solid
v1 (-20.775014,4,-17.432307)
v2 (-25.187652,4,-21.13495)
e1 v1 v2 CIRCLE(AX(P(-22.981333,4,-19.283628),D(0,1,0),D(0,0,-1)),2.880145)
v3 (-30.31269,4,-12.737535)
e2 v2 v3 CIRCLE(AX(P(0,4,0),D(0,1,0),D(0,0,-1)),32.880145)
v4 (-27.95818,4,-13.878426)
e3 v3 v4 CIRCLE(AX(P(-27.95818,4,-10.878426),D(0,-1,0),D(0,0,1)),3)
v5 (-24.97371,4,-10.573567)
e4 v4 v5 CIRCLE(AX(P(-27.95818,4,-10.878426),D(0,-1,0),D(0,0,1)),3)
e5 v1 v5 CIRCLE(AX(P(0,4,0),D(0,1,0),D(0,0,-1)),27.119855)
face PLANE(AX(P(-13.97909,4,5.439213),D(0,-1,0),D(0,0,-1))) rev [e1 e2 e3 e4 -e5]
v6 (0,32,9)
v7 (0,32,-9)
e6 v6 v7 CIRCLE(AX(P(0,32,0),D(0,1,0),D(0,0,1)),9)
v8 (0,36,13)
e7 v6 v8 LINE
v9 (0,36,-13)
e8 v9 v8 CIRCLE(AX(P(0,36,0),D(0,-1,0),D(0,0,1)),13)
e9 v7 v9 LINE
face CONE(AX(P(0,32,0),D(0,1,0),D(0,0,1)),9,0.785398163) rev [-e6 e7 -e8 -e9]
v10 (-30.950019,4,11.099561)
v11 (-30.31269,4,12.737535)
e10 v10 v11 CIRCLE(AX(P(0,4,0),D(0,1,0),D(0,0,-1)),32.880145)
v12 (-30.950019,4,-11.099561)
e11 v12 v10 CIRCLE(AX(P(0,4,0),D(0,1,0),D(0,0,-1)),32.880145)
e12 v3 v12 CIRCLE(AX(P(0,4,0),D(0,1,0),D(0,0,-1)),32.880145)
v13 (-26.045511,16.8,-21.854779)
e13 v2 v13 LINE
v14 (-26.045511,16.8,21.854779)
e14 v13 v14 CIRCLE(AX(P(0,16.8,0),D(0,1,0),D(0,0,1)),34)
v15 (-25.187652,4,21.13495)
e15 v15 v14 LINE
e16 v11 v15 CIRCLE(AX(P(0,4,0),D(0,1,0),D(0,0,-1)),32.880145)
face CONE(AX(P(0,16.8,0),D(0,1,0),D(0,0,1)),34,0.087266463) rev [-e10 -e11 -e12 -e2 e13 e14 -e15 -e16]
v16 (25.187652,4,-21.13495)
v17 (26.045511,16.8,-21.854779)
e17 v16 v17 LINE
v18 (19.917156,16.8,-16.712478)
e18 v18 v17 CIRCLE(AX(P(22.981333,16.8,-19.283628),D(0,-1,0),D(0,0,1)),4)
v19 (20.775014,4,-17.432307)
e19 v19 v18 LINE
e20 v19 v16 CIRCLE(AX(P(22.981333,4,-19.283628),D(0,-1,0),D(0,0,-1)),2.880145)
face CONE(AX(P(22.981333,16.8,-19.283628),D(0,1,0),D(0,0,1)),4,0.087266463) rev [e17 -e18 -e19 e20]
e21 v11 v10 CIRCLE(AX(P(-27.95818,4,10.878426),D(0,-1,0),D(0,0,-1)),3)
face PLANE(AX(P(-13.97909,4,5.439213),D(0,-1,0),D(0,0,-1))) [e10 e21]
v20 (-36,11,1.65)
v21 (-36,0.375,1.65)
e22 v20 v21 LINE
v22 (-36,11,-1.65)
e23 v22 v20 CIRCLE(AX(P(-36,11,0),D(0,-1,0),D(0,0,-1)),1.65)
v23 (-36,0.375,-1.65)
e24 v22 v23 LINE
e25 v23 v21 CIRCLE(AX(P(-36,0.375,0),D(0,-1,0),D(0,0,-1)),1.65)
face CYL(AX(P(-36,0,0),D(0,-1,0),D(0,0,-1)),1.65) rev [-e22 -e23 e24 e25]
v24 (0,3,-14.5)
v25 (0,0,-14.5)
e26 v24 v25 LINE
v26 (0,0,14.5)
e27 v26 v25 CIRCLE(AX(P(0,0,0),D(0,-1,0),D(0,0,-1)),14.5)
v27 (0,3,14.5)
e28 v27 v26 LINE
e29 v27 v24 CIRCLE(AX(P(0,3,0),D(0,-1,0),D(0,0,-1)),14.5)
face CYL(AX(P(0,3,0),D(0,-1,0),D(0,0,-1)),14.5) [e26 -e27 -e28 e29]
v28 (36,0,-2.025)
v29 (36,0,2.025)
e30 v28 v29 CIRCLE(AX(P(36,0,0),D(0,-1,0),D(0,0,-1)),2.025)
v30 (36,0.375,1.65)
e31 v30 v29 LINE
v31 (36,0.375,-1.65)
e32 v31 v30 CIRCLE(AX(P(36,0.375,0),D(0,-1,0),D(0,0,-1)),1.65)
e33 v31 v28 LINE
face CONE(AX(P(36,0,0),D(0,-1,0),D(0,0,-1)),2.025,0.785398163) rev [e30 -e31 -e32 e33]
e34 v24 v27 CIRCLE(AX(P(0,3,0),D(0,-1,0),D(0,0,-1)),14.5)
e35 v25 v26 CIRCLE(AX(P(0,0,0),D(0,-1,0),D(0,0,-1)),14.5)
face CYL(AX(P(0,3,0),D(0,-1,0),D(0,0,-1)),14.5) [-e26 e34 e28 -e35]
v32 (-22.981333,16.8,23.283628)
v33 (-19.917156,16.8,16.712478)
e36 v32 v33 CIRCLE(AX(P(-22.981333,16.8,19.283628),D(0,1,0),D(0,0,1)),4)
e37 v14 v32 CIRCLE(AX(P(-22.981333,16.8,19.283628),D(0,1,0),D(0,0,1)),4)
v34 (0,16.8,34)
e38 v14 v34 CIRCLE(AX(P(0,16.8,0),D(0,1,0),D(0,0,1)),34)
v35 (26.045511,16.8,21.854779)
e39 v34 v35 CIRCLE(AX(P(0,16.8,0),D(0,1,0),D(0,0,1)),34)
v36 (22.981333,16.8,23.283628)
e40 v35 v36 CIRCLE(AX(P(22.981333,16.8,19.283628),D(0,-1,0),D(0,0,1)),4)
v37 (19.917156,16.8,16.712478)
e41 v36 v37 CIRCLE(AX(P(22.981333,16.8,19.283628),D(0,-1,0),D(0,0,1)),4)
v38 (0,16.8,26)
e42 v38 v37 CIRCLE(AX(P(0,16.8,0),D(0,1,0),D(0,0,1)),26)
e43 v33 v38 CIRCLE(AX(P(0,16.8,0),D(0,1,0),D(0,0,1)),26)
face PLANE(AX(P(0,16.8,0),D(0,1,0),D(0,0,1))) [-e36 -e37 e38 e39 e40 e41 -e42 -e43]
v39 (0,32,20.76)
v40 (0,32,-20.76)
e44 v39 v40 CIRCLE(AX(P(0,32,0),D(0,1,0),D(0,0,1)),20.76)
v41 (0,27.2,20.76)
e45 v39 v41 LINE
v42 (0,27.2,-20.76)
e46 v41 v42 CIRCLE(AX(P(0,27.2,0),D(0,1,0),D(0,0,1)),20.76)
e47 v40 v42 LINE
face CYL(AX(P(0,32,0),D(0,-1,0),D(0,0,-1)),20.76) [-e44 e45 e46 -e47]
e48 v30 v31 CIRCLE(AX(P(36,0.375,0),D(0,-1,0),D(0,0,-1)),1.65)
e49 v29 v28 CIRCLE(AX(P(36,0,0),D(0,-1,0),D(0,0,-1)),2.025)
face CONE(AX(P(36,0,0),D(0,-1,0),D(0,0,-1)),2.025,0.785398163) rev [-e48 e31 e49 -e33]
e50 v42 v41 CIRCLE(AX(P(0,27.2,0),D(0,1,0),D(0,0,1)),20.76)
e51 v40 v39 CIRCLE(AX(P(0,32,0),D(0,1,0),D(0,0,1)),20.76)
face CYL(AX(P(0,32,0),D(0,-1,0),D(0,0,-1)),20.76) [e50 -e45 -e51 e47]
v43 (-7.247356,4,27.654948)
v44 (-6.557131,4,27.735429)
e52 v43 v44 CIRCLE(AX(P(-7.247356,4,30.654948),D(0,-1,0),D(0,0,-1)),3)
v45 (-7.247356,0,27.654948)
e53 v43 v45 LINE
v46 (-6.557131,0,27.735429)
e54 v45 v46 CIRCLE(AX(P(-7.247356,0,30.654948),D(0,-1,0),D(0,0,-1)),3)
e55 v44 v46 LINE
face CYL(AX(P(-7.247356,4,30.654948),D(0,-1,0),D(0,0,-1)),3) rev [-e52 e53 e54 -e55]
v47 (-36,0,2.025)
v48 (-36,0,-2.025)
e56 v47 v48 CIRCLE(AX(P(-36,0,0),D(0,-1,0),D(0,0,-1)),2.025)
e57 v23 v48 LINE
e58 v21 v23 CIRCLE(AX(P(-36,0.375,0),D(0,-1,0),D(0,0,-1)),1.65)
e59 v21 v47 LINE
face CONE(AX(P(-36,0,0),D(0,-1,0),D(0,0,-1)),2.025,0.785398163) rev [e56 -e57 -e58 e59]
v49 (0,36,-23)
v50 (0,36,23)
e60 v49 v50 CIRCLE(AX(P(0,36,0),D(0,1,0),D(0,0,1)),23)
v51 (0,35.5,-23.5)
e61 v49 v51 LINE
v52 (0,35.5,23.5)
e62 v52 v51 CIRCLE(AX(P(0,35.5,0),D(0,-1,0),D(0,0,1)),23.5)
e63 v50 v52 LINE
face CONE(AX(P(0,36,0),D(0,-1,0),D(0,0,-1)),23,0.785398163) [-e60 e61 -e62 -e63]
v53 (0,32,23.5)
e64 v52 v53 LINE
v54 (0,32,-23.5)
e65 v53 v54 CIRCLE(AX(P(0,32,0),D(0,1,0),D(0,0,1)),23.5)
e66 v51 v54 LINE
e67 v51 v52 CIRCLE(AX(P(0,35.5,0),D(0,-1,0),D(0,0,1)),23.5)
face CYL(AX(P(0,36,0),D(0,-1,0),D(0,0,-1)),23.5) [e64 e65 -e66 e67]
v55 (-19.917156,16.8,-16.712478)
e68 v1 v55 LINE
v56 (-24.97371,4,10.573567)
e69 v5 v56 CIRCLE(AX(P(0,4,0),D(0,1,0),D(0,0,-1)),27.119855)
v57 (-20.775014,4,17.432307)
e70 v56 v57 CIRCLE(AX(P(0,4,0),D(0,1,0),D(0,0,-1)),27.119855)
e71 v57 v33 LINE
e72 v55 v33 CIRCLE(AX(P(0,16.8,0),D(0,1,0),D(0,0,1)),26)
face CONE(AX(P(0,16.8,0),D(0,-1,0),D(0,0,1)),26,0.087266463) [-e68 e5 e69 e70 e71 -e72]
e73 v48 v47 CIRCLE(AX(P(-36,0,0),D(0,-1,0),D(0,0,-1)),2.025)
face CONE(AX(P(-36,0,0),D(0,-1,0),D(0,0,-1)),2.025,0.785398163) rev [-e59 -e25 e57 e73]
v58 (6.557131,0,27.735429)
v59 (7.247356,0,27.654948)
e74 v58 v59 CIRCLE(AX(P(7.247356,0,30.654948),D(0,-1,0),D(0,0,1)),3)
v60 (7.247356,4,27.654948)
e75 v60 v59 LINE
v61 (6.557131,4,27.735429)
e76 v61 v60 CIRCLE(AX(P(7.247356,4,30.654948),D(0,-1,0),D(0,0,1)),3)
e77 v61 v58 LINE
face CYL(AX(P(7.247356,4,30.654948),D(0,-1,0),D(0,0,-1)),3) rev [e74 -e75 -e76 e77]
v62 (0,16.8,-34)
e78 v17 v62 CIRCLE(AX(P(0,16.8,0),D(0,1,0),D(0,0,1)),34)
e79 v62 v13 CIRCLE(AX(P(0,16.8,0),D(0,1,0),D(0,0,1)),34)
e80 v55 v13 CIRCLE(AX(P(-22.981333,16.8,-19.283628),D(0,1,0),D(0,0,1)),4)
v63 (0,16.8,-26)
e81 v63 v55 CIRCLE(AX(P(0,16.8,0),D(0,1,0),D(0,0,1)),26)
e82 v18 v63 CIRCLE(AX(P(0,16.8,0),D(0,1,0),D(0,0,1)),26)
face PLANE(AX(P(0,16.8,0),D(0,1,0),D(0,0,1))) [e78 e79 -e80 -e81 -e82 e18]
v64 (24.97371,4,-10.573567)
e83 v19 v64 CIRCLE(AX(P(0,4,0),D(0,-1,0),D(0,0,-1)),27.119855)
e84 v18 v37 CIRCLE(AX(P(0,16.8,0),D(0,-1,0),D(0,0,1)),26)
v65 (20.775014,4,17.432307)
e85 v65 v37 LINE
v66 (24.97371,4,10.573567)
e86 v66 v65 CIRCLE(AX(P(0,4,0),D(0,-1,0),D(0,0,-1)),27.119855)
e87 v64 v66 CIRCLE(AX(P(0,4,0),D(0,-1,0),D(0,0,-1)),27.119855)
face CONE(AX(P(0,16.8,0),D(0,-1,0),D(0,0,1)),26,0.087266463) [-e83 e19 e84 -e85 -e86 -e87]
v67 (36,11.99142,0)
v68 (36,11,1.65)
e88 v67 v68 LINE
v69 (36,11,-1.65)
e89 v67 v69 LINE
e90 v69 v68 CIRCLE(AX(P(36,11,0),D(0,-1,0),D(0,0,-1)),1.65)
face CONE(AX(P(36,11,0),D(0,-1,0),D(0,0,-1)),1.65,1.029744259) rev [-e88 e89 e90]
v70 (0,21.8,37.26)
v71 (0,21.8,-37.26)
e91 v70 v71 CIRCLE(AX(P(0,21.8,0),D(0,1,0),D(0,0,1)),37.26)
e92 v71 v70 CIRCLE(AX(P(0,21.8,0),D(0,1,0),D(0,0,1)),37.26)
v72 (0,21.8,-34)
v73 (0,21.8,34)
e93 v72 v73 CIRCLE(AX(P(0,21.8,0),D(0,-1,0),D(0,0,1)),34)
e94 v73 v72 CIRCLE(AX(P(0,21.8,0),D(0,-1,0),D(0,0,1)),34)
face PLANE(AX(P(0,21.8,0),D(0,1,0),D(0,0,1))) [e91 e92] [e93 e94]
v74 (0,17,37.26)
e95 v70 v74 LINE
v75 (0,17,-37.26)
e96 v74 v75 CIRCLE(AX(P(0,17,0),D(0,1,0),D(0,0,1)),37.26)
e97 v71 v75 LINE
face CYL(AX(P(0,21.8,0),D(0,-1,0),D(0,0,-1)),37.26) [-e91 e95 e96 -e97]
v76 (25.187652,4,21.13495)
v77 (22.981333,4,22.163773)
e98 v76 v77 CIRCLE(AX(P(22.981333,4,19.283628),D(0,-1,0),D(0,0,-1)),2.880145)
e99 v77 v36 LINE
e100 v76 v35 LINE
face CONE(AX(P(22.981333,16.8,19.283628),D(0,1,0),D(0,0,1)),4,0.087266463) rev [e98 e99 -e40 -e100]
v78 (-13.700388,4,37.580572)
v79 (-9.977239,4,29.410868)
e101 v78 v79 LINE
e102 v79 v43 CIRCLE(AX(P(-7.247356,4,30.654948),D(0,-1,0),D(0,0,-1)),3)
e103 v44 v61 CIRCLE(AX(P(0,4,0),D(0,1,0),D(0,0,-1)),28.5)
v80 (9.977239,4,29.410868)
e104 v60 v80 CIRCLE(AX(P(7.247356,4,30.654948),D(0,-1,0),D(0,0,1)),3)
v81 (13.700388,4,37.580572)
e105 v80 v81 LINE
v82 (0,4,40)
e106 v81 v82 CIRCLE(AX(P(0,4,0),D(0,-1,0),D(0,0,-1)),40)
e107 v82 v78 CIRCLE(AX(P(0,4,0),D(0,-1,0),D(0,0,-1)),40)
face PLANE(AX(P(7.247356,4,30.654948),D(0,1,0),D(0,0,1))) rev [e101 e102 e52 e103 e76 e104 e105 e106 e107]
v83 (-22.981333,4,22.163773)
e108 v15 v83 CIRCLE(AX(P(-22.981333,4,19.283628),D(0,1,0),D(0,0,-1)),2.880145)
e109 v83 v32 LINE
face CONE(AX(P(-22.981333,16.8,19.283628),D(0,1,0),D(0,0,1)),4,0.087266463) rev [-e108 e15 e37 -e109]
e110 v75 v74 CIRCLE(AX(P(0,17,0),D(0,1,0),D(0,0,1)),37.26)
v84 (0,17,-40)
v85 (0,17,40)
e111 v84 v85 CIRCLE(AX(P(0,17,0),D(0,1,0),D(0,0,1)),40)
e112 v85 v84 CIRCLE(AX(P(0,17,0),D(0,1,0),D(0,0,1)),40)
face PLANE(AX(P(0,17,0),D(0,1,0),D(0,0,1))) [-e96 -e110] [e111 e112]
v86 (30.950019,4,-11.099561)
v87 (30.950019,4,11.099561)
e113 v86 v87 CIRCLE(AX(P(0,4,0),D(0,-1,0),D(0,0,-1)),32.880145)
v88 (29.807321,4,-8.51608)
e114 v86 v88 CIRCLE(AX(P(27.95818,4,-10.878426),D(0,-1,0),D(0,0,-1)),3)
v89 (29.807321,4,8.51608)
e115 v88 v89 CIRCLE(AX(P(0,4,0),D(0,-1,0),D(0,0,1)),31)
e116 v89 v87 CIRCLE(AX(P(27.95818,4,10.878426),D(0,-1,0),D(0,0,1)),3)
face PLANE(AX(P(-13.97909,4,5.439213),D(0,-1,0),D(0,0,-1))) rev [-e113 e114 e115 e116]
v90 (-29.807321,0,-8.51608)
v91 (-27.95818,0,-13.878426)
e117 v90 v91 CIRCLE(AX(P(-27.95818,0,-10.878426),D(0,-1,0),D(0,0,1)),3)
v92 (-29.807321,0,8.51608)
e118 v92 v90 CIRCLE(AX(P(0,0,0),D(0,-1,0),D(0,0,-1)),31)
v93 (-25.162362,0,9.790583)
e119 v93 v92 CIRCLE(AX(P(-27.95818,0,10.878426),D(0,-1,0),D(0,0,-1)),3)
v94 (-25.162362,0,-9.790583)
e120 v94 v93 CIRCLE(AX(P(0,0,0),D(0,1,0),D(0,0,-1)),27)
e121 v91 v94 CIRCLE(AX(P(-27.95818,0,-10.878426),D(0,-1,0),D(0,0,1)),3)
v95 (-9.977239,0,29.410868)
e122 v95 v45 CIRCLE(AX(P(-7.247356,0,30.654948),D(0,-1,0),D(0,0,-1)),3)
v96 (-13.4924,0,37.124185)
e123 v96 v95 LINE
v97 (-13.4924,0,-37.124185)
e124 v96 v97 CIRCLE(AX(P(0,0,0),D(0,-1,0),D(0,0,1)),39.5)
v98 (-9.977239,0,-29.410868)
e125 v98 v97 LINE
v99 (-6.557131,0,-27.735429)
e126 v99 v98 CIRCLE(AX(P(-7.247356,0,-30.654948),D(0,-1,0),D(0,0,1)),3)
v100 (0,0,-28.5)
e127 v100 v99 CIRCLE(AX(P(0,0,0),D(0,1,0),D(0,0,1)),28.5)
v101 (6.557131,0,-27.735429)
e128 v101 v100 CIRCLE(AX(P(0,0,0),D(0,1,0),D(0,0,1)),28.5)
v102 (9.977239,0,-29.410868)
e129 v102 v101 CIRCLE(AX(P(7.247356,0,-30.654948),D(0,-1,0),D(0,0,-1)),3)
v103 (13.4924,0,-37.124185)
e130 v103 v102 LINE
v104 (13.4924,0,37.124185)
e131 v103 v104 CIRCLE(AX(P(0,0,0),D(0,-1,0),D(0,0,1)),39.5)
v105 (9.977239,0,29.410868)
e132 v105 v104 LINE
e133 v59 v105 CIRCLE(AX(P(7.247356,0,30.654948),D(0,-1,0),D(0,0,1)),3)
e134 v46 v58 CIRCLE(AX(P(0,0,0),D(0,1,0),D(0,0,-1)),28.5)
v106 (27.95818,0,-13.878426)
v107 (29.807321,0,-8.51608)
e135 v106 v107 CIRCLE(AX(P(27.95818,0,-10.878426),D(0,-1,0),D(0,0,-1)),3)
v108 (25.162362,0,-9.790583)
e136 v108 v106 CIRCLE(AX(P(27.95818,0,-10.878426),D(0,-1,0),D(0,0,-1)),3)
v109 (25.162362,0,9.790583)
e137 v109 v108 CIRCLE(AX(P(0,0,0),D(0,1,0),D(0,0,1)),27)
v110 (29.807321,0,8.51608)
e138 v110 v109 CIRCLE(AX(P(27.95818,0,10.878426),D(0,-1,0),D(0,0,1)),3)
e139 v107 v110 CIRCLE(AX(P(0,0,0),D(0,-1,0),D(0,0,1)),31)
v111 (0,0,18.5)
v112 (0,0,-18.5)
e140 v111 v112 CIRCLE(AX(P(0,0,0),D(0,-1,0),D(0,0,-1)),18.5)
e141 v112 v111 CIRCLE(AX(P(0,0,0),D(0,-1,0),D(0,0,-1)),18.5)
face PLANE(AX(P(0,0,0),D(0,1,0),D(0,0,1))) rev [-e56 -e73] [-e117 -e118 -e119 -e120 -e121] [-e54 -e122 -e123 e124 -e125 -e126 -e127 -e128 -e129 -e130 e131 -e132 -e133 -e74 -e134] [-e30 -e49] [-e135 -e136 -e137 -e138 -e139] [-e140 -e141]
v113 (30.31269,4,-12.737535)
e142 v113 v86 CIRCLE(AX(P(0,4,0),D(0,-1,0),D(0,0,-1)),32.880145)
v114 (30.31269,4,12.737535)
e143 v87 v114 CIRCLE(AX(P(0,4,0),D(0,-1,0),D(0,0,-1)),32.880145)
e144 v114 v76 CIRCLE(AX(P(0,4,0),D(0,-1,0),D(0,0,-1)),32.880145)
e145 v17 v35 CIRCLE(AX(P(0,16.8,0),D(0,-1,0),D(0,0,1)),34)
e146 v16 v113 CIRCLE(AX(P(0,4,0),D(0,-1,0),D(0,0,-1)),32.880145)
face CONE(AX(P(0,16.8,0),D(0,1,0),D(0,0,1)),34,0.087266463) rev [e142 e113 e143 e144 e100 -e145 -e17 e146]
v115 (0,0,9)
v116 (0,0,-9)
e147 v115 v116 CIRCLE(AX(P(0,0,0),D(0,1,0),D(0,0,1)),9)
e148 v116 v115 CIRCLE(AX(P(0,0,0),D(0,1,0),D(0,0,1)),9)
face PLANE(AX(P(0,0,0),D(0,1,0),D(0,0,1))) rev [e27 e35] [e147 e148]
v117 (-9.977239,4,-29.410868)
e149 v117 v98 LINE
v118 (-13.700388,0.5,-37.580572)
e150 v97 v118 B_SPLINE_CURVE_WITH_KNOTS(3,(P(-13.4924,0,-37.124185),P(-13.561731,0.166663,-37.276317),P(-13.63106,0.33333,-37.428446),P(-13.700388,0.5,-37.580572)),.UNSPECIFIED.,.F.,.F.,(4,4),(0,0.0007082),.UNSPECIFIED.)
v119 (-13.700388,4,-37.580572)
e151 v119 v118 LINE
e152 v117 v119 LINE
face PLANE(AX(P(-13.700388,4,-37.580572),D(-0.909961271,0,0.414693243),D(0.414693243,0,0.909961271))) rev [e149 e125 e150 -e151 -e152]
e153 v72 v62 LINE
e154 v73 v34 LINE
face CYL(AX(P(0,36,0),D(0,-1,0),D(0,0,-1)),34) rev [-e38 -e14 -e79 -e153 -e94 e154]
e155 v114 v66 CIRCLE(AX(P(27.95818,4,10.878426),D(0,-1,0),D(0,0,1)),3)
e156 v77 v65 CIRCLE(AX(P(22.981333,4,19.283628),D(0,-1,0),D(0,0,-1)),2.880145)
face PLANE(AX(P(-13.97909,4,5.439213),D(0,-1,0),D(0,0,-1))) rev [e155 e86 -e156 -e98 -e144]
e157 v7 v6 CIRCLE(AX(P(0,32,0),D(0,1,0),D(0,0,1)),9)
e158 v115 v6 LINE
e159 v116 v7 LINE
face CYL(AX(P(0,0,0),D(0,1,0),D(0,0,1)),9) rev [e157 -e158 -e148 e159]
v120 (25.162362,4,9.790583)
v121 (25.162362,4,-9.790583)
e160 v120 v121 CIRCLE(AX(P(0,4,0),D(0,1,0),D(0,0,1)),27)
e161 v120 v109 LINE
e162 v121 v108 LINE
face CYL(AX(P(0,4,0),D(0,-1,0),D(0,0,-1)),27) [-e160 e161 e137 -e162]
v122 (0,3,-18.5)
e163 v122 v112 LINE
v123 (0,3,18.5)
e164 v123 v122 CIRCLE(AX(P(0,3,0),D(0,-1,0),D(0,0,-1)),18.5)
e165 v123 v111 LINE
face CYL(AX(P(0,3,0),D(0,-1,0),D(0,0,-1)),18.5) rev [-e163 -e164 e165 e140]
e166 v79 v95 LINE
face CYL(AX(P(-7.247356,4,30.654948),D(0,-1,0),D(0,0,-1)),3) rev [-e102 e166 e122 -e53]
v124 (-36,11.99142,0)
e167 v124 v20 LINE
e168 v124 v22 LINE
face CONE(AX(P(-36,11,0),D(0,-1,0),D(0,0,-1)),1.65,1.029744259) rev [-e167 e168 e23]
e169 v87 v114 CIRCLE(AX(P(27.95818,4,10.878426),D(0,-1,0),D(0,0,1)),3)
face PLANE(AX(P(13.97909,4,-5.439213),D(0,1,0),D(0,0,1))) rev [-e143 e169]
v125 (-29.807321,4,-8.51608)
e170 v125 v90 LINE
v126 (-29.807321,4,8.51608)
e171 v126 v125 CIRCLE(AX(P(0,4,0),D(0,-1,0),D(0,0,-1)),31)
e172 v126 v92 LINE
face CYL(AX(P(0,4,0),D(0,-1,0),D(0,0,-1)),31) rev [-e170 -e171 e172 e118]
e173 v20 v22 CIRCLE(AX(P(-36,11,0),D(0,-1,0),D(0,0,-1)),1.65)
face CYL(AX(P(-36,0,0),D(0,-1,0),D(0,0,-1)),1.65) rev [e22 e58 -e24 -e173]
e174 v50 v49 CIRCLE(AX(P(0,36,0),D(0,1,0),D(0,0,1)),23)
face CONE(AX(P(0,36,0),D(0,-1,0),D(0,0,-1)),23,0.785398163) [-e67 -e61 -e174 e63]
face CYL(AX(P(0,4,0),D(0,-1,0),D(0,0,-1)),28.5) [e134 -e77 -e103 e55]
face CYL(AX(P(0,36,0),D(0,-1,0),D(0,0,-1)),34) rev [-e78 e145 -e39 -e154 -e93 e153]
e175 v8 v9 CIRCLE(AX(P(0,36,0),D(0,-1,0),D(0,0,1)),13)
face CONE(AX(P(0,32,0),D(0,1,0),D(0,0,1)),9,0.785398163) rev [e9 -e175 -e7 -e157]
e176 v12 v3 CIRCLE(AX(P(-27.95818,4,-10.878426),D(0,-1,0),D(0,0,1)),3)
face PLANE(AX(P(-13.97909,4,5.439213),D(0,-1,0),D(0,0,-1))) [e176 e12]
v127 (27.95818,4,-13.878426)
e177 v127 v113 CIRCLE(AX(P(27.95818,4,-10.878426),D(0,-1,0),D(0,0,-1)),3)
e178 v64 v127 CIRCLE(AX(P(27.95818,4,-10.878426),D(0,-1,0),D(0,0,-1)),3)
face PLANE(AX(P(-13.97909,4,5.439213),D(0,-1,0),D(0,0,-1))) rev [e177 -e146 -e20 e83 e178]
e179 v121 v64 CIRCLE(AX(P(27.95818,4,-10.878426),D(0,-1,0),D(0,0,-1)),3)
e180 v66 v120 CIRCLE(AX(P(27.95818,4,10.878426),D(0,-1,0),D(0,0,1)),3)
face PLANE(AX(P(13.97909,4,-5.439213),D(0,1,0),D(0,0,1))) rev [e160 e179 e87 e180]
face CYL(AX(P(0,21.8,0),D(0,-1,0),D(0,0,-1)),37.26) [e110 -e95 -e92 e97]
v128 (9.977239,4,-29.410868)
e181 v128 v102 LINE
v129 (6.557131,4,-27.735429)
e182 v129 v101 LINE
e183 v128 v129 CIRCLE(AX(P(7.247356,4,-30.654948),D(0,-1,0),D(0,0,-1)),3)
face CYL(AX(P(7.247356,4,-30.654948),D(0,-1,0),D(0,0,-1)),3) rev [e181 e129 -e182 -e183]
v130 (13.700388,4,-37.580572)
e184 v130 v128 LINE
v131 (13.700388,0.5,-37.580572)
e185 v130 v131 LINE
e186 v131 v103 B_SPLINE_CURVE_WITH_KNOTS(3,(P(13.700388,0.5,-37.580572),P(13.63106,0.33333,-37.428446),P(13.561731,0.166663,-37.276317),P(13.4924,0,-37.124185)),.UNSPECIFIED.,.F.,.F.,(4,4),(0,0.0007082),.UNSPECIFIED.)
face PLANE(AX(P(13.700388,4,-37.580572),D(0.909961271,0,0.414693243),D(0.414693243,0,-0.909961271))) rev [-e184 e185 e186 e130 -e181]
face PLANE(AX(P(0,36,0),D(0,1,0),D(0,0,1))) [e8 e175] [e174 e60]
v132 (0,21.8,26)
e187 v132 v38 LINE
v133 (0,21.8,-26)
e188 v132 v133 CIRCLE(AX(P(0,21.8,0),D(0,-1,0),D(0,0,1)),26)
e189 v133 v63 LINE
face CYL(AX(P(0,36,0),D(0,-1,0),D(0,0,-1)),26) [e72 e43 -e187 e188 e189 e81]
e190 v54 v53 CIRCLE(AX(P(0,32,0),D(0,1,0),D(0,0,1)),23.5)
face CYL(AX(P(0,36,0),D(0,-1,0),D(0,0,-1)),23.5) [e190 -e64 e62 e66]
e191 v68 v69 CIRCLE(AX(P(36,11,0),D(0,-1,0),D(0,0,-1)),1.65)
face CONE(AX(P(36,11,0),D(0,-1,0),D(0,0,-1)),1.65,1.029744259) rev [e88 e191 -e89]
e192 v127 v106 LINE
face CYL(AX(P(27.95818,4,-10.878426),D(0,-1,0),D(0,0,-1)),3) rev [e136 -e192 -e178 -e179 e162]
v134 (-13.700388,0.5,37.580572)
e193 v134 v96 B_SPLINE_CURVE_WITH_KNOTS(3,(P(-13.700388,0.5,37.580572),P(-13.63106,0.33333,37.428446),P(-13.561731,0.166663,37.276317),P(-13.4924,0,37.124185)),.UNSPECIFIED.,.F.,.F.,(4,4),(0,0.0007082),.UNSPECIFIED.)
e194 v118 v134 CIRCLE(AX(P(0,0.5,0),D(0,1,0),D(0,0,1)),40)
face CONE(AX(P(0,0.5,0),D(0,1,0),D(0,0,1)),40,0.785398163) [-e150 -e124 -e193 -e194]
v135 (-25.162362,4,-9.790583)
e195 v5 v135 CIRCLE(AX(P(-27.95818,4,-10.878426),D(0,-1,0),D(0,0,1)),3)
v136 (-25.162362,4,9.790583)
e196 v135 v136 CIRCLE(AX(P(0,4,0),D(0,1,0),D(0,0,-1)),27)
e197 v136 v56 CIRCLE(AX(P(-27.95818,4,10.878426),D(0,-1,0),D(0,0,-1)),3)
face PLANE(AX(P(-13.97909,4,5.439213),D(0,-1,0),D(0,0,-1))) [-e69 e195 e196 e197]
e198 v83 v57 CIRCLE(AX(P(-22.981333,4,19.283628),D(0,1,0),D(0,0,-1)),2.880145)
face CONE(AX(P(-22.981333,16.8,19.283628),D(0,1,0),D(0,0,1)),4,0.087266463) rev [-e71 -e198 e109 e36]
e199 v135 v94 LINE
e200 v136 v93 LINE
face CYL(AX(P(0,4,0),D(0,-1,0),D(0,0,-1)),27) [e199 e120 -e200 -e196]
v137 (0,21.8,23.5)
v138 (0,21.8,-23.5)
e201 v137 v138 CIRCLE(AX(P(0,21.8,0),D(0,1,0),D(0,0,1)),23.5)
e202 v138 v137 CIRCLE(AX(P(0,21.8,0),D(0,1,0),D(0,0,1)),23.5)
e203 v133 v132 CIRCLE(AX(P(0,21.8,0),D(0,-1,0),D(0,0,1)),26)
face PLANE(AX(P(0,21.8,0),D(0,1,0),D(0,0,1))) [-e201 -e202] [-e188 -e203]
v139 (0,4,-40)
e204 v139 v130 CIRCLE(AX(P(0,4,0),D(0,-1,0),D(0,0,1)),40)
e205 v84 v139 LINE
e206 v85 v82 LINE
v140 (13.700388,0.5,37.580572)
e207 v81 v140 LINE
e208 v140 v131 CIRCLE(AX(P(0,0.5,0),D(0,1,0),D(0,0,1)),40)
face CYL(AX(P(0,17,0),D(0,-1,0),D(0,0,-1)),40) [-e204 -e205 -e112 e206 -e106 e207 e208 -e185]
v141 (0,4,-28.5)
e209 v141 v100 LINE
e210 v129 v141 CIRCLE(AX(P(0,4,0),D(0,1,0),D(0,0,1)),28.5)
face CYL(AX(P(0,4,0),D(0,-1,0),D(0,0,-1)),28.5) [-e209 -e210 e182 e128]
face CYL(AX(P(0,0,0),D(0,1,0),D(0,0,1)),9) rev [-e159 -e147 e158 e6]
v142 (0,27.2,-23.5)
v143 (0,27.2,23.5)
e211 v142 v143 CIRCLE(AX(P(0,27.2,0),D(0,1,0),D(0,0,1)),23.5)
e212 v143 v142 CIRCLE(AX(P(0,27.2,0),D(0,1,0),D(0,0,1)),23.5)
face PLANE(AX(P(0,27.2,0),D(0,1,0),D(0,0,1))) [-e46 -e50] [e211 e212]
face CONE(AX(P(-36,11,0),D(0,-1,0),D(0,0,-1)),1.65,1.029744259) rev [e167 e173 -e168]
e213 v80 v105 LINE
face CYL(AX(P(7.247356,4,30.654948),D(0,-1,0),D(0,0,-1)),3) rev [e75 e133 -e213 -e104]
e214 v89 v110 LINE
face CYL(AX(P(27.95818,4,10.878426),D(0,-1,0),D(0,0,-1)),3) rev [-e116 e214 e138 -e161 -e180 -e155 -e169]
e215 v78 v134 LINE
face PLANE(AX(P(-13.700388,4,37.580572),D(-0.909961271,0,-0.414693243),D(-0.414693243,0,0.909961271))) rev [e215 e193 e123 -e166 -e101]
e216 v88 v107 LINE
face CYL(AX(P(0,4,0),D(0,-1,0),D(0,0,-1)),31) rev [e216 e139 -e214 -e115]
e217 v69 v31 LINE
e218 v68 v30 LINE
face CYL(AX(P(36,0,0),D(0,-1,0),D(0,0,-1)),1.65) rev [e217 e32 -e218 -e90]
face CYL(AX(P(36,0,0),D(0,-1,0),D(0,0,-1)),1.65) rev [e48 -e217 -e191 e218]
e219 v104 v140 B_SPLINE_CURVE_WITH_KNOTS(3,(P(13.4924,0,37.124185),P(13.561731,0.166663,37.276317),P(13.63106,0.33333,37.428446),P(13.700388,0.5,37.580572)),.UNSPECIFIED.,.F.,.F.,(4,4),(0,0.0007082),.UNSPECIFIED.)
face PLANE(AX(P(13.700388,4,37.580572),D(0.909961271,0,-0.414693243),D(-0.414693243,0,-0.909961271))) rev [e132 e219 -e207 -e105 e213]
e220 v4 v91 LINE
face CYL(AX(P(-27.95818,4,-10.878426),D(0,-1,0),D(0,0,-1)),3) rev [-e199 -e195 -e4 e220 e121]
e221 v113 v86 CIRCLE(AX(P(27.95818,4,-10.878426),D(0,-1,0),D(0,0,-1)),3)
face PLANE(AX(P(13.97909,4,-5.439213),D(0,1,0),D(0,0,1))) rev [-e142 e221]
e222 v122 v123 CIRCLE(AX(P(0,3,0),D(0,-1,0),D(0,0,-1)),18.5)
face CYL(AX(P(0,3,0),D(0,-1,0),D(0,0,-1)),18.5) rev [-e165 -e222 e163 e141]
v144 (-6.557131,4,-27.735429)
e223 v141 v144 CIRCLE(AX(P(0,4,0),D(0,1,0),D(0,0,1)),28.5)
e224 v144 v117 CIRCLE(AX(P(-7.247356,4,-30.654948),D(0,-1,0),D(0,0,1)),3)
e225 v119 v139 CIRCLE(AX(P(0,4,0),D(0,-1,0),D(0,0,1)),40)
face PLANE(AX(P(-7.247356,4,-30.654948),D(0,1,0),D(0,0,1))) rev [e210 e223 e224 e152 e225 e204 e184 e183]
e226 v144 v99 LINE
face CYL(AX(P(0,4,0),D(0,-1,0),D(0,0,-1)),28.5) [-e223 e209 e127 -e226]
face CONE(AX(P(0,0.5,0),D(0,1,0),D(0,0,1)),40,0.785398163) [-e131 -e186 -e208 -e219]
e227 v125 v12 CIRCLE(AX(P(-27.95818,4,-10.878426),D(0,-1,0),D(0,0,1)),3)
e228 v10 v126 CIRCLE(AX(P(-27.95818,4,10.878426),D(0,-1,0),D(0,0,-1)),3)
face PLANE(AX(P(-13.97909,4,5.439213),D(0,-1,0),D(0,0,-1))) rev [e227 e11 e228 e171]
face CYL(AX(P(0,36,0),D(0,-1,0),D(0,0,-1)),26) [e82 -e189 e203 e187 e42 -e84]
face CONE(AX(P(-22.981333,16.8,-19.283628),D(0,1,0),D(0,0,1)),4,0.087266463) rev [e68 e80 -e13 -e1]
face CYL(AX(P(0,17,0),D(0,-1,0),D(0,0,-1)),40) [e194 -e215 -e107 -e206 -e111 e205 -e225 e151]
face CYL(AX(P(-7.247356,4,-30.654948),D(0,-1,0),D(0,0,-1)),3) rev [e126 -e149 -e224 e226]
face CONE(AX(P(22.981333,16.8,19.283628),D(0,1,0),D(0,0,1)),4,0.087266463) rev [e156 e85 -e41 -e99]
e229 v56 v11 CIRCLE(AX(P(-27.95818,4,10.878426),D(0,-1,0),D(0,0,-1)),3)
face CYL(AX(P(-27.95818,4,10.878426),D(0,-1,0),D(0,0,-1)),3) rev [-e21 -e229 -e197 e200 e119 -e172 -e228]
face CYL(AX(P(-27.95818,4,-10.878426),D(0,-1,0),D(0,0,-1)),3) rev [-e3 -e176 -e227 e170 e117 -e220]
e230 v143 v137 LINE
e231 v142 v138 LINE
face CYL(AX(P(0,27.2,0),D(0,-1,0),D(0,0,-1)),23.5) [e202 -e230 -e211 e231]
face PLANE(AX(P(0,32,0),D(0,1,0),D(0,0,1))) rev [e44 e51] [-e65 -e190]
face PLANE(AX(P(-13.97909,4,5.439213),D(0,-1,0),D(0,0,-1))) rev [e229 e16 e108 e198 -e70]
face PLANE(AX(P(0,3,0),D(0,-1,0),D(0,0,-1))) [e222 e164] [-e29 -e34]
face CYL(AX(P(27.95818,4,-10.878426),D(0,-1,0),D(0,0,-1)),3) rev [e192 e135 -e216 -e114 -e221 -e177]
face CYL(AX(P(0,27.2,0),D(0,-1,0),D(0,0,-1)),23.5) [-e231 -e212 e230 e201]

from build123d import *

# Parameters (mm, degrees)
SKETCH1_R                   = 40
BOSS_EXTRUDE1_DEPTH         = 17
SKETCH2_R                   = 37.26
BOSS_EXTRUDE2_DEPTH         = 4.8
SKETCH3_R                   = 23.5
BOSS_EXTRUDE3_DEPTH         = 5.4
SKETCH4_R                   = 20.76
BOSS_EXTRUDE4_DEPTH         = 4.8
SKETCH5_R                   = 23.5
BOSS_EXTRUDE5_DEPTH         = 4
CUT_EXTRUDE1_DEPTH          = 68.052218457
CUT_EXTRUDE1_DEPTH_BACK     = 68.052218457
SKETCH6_R                   = 9
CHAMFER1_SIZE               = 4
CUT_EXTRUDE2_DEPTH          = 61.623757719
CUT_EXTRUDE2_DEPTH_BACK     = 5
SKETCH7_R                   = 34
SKETCH7_R_2                 = 26
CUT_EXTRUDE3_DEPTH          = 4
CUT_EXTRUDE4_DEPTH          = 12.8
CUT_EXTRUDE4_DRAFT          = -5
MIRROR1_COPY_1_DEPTH        = 12.8
MIRROR1_COPY_1_DRAFT        = -5
M4_TAPPED_HOLE1_D           = 3.3
M4_TAPPED_HOLE1_DEPTH       = 11
M4_TAPPED_HOLE1_CSINK_D     = 4.05
M4_TAPPED_HOLE1_CSINK_ANGLE = 90
M4_TAPPED_HOLE1_TIP         = 0.991420021
CUT_EXTRUDE5_DEPTH          = 4
SKETCH15_R                  = 18.5
SKETCH15_R_2                = 14.5
CUT_EXTRUDE6_DEPTH          = 3
CHAMFER2_SIZE               = 0.5


with BuildPart() as part:
    # Sketch1 → Boss-Extrude1 (new body)
    with BuildSketch(Plane(origin=(0, 0, 0), x_dir=(1, 0, 0), z_dir=(0, 1, 0))):
        with Locations(Location((0, 0, 0), (0, 0, 270))):
            Circle(SKETCH1_R)
    extrude(amount=BOSS_EXTRUDE1_DEPTH)

    # Sketch2 → Boss-Extrude2 (add)
    with BuildSketch(Plane(origin=(0, 17, 0), x_dir=(1, 0, 0), z_dir=(0, 1, 0))):
        with Locations(Location((0, 0, 0), (0, 0, 270))):
            Circle(SKETCH2_R)
    extrude(amount=BOSS_EXTRUDE2_DEPTH)

    # Sketch3 → Boss-Extrude3 (add)
    with BuildSketch(Plane(origin=(0, 21.8, 0), x_dir=(1, 0, 0), z_dir=(0, 1, 0))):
        with Locations(Location((0, 0, 0), (0, 0, 270))):
            Circle(SKETCH3_R)
    extrude(amount=BOSS_EXTRUDE3_DEPTH)

    # Sketch4 → Boss-Extrude4 (add)
    with BuildSketch(Plane(origin=(0, 27.2, 0), x_dir=(1, 0, 0), z_dir=(0, 1, 0))):
        with Locations(Location((0, 0, 0), (0, 0, 270))):
            Circle(SKETCH4_R)
    extrude(amount=BOSS_EXTRUDE4_DEPTH)

    # Sketch5 → Boss-Extrude5 (add)
    with BuildSketch(Plane(origin=(0, 32, 0), x_dir=(1, 0, 0), z_dir=(0, 1, 0))):
        with Locations(Location((0, 0, 0), (0, 0, 270))):
            Circle(SKETCH5_R)
    extrude(amount=BOSS_EXTRUDE5_DEPTH)

    # Sketch6 → Cut-Extrude1 (cut, two sides: drawn at the far end of the back side and taken through both)
    with BuildSketch(Plane(origin=(0, 36, 0), x_dir=(1, 0, 0), z_dir=(0, 1, 0)).offset(-CUT_EXTRUDE1_DEPTH_BACK)):
        with Locations(Location((0, 0, 0), (0, 0, 270))):
            Circle(SKETCH6_R)
    extrude(amount=CUT_EXTRUDE1_DEPTH + CUT_EXTRUDE1_DEPTH_BACK, mode=Mode.SUBTRACT)

    # Chamfer1
    chamfer1_edges = [part.edges().sort_by_distance(p)[0] for p in [
        (0, 36, -9),
    ]]
    chamfer(chamfer1_edges, length=CHAMFER1_SIZE)

    # Sketch7 → Cut-Extrude2 (cut, two sides: drawn at the far end of the back side and taken through both)
    with BuildSketch(Plane(origin=(0, 21.8, 0), x_dir=(1, 0, 0), z_dir=(0, 1, 0)).offset(-CUT_EXTRUDE2_DEPTH_BACK)):
        with Locations(Location((0, 0, 0), (0, 0, 270))):
            Circle(SKETCH7_R)
        with Locations(Location((0, 0, 0), (0, 0, 270))):
            Circle(SKETCH7_R_2, mode=Mode.SUBTRACT)
    extrude(amount=CUT_EXTRUDE2_DEPTH + CUT_EXTRUDE2_DEPTH_BACK, mode=Mode.SUBTRACT)

    # Sketch8 → Cut-Extrude3 (cut)
    with BuildSketch(Plane(origin=(0, 0, 0), x_dir=(-1, 0, 0), z_dir=(0, -1, 0))):
        with BuildLine():
            ThreePointArc((25.162362394, -9.790583167), (27, 0), (25.162362394, 9.790583167))
            ThreePointArc((25.162362394, 9.790583167), (28.751993608, 13.771496887), (29.807321036, 8.516079652))
            ThreePointArc((29.807321036, 8.516079652), (31, 0), (29.807321036, -8.516079652))
            ThreePointArc((29.807321036, -8.516079652), (28.751993608, -13.771496887), (25.162362394, -9.790583167))
        make_face()
        with BuildLine():
            ThreePointArc((-25.162362394, 9.790583167), (-28.751993608, 13.771496887), (-29.807321036, 8.516079652))
            ThreePointArc((-29.807321036, 8.516079652), (-31, 0), (-29.807321036, -8.516079652))
            ThreePointArc((-29.807321036, -8.516079652), (-28.751993608, -13.771496887), (-25.162362394, -9.790583167))
            ThreePointArc((-25.162362394, -9.790583167), (-27, 0), (-25.162362394, 9.790583167))
        make_face()
    extrude(amount=-CUT_EXTRUDE3_DEPTH, mode=Mode.SUBTRACT)


with BuildPart() as cut_extrude4_tool:
    # Sketch9 → Cut-Extrude4 (with draft: the straight prism first)
    with BuildSketch(Plane(origin=(0, 16.8, 0), x_dir=(1, 0, 0), z_dir=(0, 1, 0))):
        with BuildLine():
            ThreePointArc((-26.045511066, 21.854778729), (-34, 0), (-26.045511066, -21.854778729))
            ThreePointArc((-26.045511066, -21.854778729), (-20.410182855, -22.347806063), (-19.917155521, -16.712477852))
            ThreePointArc((-19.917155521, -16.712477852), (-26, 0), (-19.917155521, 16.712477852))
            ThreePointArc((-19.917155521, 16.712477852), (-20.410182855, 22.347806063), (-26.045511066, 21.854778729))
        make_face()
    extrude(amount=-CUT_EXTRUDE4_DEPTH)
    # Cut-Extrude4: the draft: its side faces are tilted about the plane it starts from
    cut_extrude4_sides = [cut_extrude4_tool.faces().sort_by_distance(p)[0] for p in [
        (-20.410182855, 10.4, 22.347806063),
        (-26, 10.4, 0),
        (-20.410182855, 10.4, -22.347806063),
        (-34, 10.4, 0),
    ]]
    draft(cut_extrude4_sides, Plane(origin=(0, 16.8, 0), x_dir=(1, 0, 0), z_dir=(0, 1, 0)), CUT_EXTRUDE4_DRAFT)


with BuildPart() as part_1:
    add(part.part)

    # Cut-Extrude4: cut by cut_extrude4_tool
    add(cut_extrude4_tool.part, mode=Mode.SUBTRACT)


with BuildPart() as mirror1_copy_1_tool:
    # Mirror1 copy 1 sketch → Mirror1 copy 1 (with draft: the straight prism first)
    with BuildSketch(Plane(origin=(0, 16.8, 0), x_dir=(-1, 0, 0), z_dir=(0, 1, 0))):
        with BuildLine():
            ThreePointArc((-26.045511066, -21.854778729), (-34, 0), (-26.045511066, 21.854778729))
            ThreePointArc((-26.045511066, 21.854778729), (-20.410182855, 22.347806063), (-19.917155521, 16.712477852))
            ThreePointArc((-19.917155521, 16.712477852), (-26, 0), (-19.917155521, -16.712477852))
            ThreePointArc((-19.917155521, -16.712477852), (-20.410182855, -22.347806063), (-26.045511066, -21.854778729))
        make_face()
    extrude(amount=-MIRROR1_COPY_1_DEPTH)
    # Mirror1 copy 1: the draft: its side faces are tilted about the plane it starts from
    mirror1_copy_1_sides = [mirror1_copy_1_tool.faces().sort_by_distance(p)[0] for p in [
        (20.410182855, 10.4, 22.347806063),
        (26, 10.4, 0),
        (20.410182855, 10.4, -22.347806063),
        (34, 10.4, 0),
    ]]
    draft(mirror1_copy_1_sides, Plane(origin=(0, 16.8, 0), x_dir=(-1, 0, 0), z_dir=(0, 1, 0)), MIRROR1_COPY_1_DRAFT)


with BuildPart() as part_2:
    add(part_1.part)

    # Mirror1 copy 1: cut by mirror1_copy_1_tool
    add(mirror1_copy_1_tool.part, mode=Mode.SUBTRACT)

    # M4 Tapped Hole1
    with Locations(Plane(origin=(0, 0, 0), x_dir=(-1, 0, 0), z_dir=(0, -1, 0))):
        with Locations((36, 0), (-36, 0)):
            CounterSinkHole(M4_TAPPED_HOLE1_D / 2, M4_TAPPED_HOLE1_CSINK_D / 2, depth=M4_TAPPED_HOLE1_DEPTH, counter_sink_angle=M4_TAPPED_HOLE1_CSINK_ANGLE)
            with Locations((0, 0, -(M4_TAPPED_HOLE1_DEPTH + M4_TAPPED_HOLE1_TIP / 2))):  # 118° drill point
                Cone(0, M4_TAPPED_HOLE1_D / 2, M4_TAPPED_HOLE1_TIP, mode=Mode.SUBTRACT)

    # Sketch14 → Cut-Extrude5 (cut)
    with BuildSketch(Plane(origin=(0, 0, 0), x_dir=(-1, 0, 0), z_dir=(0, -1, 0))):
        with BuildLine():
            Line((13.700387767, -37.580571776), (9.977239383, -29.410868278))
            ThreePointArc((9.977239383, -29.410868278), (8.567138417, -27.960848297), (6.557131231, -27.735429148))
            ThreePointArc((6.557131231, -27.735429148), (0, -28.5), (-6.557131231, -27.735429148))
            ThreePointArc((-6.557131231, -27.735429148), (-8.567138417, -27.960848297), (-9.977239383, -29.410868278))
            Line((-9.977239383, -29.410868278), (-13.700387767, -37.580571776))
            ThreePointArc((-13.700387767, -37.580571776), (0, -40), (13.700387767, -37.580571776))
        make_face()
        with BuildLine():
            Line((-13.700387767, 37.580571776), (-9.977239383, 29.410868278))
            ThreePointArc((-9.977239383, 29.410868278), (-8.567138417, 27.960848297), (-6.557131231, 27.735429148))
            ThreePointArc((-6.557131231, 27.735429148), (0, 28.5), (6.557131231, 27.735429148))
            ThreePointArc((6.557131231, 27.735429148), (8.567138417, 27.960848297), (9.977239383, 29.410868278))
            Line((9.977239383, 29.410868278), (13.700387767, 37.580571776))
            ThreePointArc((13.700387767, 37.580571776), (0, 40), (-13.700387767, 37.580571776))
        make_face()
    extrude(amount=-CUT_EXTRUDE5_DEPTH, mode=Mode.SUBTRACT)

    # Sketch15 → Cut-Extrude6 (cut)
    with BuildSketch(Plane(origin=(0, 0, 0), x_dir=(-1, 0, 0), z_dir=(0, -1, 0))):
        with Locations(Location((0, 0, 0), (0, 0, 90))):
            Circle(SKETCH15_R)
        with Locations(Location((0, 0, 0), (0, 0, 90))):
            Circle(SKETCH15_R_2, mode=Mode.SUBTRACT)
    extrude(amount=-CUT_EXTRUDE6_DEPTH, mode=Mode.SUBTRACT)

    # Chamfer2
    chamfer2_edges = [part_2.edges().sort_by_distance(p)[0] for p in [
        (-40, 0, 0),
        (40, 0, 0),
        (0, 36, -23.5),
    ]]
    chamfer(chamfer2_edges, length=CHAMFER2_SIZE)


solid = part_2.part
